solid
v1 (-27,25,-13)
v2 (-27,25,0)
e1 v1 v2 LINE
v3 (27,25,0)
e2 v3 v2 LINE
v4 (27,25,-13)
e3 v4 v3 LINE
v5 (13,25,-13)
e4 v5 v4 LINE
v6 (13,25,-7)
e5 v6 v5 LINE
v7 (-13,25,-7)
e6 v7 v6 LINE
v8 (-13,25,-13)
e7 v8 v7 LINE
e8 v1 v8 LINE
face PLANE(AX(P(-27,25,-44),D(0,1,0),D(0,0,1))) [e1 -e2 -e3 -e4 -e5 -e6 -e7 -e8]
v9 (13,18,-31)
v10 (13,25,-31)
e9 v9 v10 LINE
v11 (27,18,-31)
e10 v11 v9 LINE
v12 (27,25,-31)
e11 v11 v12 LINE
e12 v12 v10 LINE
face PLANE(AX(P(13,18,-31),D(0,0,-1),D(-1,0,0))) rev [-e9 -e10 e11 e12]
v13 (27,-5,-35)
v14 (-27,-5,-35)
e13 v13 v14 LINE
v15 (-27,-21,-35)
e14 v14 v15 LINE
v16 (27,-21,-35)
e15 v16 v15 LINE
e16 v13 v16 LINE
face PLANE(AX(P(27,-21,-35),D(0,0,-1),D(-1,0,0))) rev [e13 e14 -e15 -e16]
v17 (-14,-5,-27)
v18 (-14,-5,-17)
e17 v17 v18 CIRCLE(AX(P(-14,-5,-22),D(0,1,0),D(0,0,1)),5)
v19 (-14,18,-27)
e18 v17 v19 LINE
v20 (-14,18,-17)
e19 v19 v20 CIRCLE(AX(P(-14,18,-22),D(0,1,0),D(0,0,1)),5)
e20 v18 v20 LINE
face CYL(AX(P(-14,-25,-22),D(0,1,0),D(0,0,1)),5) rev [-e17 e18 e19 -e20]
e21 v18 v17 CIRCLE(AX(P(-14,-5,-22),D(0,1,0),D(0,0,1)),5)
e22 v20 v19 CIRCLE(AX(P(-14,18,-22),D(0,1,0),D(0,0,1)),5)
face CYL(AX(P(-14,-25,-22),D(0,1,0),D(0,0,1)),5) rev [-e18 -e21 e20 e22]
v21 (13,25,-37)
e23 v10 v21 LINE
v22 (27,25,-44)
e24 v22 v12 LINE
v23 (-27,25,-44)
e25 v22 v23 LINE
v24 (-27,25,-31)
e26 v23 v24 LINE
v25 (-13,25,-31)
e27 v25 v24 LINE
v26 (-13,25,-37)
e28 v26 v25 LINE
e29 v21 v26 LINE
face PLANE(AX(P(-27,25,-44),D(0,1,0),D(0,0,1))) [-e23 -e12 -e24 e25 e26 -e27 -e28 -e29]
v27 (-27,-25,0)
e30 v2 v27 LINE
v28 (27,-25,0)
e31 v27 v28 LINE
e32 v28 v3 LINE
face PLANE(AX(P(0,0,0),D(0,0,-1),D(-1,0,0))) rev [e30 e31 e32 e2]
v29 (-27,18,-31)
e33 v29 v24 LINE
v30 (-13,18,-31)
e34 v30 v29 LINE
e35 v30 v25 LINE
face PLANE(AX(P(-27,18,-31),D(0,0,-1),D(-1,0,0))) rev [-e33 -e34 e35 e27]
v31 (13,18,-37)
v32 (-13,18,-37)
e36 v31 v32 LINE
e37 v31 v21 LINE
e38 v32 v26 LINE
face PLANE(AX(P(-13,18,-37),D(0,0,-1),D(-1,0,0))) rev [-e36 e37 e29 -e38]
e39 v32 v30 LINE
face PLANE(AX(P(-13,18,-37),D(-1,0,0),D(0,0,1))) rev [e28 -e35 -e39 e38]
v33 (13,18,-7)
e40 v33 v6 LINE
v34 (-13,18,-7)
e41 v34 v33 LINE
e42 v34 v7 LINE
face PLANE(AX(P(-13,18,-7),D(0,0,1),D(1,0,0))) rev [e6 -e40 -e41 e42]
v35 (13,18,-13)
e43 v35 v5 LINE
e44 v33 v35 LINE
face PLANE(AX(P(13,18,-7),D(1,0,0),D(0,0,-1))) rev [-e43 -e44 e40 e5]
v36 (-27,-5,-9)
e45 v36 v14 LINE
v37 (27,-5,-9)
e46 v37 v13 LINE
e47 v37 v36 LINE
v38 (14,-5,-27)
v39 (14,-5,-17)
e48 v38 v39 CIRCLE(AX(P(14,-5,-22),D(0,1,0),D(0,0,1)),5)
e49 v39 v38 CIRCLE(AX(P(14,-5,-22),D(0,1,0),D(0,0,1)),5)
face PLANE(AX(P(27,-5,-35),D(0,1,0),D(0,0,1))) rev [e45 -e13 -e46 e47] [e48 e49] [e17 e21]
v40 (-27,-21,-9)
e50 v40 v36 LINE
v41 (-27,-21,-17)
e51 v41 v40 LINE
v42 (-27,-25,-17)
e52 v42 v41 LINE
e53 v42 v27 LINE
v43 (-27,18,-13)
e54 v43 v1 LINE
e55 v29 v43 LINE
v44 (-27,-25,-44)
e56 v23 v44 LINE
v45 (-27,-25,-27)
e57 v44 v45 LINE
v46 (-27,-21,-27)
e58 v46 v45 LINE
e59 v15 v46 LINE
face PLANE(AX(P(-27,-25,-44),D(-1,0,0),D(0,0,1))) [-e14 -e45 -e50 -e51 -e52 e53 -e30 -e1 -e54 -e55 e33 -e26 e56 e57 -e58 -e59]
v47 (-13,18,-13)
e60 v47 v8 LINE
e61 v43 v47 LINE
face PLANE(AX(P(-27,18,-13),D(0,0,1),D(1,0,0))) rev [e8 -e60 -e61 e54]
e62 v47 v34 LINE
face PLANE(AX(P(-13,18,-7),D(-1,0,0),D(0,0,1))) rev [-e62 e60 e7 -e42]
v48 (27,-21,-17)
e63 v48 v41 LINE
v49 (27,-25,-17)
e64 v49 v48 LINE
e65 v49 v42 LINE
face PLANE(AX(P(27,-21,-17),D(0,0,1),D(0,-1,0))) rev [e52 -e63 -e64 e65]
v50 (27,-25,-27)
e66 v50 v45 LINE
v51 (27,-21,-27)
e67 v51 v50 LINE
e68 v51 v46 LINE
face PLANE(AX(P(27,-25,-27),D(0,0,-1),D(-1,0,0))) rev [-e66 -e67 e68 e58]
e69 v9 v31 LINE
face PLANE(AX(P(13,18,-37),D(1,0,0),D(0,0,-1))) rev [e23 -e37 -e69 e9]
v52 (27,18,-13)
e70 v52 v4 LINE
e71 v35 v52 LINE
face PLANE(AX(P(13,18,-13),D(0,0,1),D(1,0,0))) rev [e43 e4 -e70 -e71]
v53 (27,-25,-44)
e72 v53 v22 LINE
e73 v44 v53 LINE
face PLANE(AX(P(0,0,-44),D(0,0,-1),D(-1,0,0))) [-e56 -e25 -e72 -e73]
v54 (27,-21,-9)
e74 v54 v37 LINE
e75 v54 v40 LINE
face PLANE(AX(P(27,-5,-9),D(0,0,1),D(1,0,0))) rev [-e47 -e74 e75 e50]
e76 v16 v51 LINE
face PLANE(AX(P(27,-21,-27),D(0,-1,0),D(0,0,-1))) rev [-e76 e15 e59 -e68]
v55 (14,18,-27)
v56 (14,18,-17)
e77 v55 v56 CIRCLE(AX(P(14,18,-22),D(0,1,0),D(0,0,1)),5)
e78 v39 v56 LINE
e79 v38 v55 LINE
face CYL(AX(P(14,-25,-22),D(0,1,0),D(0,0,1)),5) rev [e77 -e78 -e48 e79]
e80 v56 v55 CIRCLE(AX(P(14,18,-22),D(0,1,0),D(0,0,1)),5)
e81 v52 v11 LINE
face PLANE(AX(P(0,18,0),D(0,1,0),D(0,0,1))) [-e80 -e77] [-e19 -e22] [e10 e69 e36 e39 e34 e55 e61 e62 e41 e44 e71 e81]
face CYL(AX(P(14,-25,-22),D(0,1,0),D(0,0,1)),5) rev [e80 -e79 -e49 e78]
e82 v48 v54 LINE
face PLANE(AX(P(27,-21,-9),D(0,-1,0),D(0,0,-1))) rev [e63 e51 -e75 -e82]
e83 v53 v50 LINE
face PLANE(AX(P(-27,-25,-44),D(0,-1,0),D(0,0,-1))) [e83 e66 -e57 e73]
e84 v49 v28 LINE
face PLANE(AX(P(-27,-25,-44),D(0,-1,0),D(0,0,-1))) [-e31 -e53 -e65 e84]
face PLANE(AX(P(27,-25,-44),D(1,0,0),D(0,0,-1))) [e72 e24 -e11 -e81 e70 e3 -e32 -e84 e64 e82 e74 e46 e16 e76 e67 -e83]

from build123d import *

# Parameters (mm, degrees)
BASE_BLOCK_SKETCH_W       = 54
BASE_BLOCK_SKETCH_H       = 50
BASE_BLOCK_54X50X44_DEPTH = 44
TOP_POCKET_7_DEEP_DEPTH   = 7
T_SLOT_CUT_DEPTH          = 75.006756448
POCKET_HOLES_SKETCH_R     = 5
POCKET_HOLES_2X_10_DEPTH  = 68.186308129


with BuildPart() as part:
    # Base Block Sketch → Base Block 54x50x44 (new body)
    with BuildSketch(Plane.XY):
        Rectangle(BASE_BLOCK_SKETCH_W, BASE_BLOCK_SKETCH_H)
    extrude(amount=-BASE_BLOCK_54X50X44_DEPTH)

    # Top Pocket Sketch → Top Pocket 7 Deep (cut)
    with BuildSketch(Plane(origin=(0, 25, 0), x_dir=(1, 0, 0), z_dir=(0, 1, 0))):
        Polygon((-13, 37), (13, 37), (13, 31), (27, 31), (27, 13), (13, 13), (13, 7), (-13, 7), (-13, 13), (-27, 13), (-27, 31), (-13, 31), align=None)
    extrude(amount=-TOP_POCKET_7_DEEP_DEPTH, mode=Mode.SUBTRACT)

    # T-Slot Sketch → T-Slot Cut (cut, through all)
    with BuildSketch(Plane.ZY.offset(27)):
        Polygon((-27, -25), (-27, -21), (-35, -21), (-35, -5), (-9, -5), (-9, -21), (-17, -21), (-17, -25), align=None)
    extrude(amount=-T_SLOT_CUT_DEPTH, mode=Mode.SUBTRACT)

    # Pocket Holes Sketch → Pocket Holes 2xØ10 (cut, through all)
    with BuildSketch(Plane(origin=(0, 18, 0), x_dir=(1, 0, 0), z_dir=(0, 1, 0))):
        with Locations(Location((-14, 22, 0), (0, 0, 270))):
            Circle(POCKET_HOLES_SKETCH_R)
        with Locations(Location((14, 22, 0), (0, 0, 270))):
            Circle(POCKET_HOLES_SKETCH_R)
    extrude(amount=-POCKET_HOLES_2X_10_DEPTH, mode=Mode.SUBTRACT)


solid = part.part
